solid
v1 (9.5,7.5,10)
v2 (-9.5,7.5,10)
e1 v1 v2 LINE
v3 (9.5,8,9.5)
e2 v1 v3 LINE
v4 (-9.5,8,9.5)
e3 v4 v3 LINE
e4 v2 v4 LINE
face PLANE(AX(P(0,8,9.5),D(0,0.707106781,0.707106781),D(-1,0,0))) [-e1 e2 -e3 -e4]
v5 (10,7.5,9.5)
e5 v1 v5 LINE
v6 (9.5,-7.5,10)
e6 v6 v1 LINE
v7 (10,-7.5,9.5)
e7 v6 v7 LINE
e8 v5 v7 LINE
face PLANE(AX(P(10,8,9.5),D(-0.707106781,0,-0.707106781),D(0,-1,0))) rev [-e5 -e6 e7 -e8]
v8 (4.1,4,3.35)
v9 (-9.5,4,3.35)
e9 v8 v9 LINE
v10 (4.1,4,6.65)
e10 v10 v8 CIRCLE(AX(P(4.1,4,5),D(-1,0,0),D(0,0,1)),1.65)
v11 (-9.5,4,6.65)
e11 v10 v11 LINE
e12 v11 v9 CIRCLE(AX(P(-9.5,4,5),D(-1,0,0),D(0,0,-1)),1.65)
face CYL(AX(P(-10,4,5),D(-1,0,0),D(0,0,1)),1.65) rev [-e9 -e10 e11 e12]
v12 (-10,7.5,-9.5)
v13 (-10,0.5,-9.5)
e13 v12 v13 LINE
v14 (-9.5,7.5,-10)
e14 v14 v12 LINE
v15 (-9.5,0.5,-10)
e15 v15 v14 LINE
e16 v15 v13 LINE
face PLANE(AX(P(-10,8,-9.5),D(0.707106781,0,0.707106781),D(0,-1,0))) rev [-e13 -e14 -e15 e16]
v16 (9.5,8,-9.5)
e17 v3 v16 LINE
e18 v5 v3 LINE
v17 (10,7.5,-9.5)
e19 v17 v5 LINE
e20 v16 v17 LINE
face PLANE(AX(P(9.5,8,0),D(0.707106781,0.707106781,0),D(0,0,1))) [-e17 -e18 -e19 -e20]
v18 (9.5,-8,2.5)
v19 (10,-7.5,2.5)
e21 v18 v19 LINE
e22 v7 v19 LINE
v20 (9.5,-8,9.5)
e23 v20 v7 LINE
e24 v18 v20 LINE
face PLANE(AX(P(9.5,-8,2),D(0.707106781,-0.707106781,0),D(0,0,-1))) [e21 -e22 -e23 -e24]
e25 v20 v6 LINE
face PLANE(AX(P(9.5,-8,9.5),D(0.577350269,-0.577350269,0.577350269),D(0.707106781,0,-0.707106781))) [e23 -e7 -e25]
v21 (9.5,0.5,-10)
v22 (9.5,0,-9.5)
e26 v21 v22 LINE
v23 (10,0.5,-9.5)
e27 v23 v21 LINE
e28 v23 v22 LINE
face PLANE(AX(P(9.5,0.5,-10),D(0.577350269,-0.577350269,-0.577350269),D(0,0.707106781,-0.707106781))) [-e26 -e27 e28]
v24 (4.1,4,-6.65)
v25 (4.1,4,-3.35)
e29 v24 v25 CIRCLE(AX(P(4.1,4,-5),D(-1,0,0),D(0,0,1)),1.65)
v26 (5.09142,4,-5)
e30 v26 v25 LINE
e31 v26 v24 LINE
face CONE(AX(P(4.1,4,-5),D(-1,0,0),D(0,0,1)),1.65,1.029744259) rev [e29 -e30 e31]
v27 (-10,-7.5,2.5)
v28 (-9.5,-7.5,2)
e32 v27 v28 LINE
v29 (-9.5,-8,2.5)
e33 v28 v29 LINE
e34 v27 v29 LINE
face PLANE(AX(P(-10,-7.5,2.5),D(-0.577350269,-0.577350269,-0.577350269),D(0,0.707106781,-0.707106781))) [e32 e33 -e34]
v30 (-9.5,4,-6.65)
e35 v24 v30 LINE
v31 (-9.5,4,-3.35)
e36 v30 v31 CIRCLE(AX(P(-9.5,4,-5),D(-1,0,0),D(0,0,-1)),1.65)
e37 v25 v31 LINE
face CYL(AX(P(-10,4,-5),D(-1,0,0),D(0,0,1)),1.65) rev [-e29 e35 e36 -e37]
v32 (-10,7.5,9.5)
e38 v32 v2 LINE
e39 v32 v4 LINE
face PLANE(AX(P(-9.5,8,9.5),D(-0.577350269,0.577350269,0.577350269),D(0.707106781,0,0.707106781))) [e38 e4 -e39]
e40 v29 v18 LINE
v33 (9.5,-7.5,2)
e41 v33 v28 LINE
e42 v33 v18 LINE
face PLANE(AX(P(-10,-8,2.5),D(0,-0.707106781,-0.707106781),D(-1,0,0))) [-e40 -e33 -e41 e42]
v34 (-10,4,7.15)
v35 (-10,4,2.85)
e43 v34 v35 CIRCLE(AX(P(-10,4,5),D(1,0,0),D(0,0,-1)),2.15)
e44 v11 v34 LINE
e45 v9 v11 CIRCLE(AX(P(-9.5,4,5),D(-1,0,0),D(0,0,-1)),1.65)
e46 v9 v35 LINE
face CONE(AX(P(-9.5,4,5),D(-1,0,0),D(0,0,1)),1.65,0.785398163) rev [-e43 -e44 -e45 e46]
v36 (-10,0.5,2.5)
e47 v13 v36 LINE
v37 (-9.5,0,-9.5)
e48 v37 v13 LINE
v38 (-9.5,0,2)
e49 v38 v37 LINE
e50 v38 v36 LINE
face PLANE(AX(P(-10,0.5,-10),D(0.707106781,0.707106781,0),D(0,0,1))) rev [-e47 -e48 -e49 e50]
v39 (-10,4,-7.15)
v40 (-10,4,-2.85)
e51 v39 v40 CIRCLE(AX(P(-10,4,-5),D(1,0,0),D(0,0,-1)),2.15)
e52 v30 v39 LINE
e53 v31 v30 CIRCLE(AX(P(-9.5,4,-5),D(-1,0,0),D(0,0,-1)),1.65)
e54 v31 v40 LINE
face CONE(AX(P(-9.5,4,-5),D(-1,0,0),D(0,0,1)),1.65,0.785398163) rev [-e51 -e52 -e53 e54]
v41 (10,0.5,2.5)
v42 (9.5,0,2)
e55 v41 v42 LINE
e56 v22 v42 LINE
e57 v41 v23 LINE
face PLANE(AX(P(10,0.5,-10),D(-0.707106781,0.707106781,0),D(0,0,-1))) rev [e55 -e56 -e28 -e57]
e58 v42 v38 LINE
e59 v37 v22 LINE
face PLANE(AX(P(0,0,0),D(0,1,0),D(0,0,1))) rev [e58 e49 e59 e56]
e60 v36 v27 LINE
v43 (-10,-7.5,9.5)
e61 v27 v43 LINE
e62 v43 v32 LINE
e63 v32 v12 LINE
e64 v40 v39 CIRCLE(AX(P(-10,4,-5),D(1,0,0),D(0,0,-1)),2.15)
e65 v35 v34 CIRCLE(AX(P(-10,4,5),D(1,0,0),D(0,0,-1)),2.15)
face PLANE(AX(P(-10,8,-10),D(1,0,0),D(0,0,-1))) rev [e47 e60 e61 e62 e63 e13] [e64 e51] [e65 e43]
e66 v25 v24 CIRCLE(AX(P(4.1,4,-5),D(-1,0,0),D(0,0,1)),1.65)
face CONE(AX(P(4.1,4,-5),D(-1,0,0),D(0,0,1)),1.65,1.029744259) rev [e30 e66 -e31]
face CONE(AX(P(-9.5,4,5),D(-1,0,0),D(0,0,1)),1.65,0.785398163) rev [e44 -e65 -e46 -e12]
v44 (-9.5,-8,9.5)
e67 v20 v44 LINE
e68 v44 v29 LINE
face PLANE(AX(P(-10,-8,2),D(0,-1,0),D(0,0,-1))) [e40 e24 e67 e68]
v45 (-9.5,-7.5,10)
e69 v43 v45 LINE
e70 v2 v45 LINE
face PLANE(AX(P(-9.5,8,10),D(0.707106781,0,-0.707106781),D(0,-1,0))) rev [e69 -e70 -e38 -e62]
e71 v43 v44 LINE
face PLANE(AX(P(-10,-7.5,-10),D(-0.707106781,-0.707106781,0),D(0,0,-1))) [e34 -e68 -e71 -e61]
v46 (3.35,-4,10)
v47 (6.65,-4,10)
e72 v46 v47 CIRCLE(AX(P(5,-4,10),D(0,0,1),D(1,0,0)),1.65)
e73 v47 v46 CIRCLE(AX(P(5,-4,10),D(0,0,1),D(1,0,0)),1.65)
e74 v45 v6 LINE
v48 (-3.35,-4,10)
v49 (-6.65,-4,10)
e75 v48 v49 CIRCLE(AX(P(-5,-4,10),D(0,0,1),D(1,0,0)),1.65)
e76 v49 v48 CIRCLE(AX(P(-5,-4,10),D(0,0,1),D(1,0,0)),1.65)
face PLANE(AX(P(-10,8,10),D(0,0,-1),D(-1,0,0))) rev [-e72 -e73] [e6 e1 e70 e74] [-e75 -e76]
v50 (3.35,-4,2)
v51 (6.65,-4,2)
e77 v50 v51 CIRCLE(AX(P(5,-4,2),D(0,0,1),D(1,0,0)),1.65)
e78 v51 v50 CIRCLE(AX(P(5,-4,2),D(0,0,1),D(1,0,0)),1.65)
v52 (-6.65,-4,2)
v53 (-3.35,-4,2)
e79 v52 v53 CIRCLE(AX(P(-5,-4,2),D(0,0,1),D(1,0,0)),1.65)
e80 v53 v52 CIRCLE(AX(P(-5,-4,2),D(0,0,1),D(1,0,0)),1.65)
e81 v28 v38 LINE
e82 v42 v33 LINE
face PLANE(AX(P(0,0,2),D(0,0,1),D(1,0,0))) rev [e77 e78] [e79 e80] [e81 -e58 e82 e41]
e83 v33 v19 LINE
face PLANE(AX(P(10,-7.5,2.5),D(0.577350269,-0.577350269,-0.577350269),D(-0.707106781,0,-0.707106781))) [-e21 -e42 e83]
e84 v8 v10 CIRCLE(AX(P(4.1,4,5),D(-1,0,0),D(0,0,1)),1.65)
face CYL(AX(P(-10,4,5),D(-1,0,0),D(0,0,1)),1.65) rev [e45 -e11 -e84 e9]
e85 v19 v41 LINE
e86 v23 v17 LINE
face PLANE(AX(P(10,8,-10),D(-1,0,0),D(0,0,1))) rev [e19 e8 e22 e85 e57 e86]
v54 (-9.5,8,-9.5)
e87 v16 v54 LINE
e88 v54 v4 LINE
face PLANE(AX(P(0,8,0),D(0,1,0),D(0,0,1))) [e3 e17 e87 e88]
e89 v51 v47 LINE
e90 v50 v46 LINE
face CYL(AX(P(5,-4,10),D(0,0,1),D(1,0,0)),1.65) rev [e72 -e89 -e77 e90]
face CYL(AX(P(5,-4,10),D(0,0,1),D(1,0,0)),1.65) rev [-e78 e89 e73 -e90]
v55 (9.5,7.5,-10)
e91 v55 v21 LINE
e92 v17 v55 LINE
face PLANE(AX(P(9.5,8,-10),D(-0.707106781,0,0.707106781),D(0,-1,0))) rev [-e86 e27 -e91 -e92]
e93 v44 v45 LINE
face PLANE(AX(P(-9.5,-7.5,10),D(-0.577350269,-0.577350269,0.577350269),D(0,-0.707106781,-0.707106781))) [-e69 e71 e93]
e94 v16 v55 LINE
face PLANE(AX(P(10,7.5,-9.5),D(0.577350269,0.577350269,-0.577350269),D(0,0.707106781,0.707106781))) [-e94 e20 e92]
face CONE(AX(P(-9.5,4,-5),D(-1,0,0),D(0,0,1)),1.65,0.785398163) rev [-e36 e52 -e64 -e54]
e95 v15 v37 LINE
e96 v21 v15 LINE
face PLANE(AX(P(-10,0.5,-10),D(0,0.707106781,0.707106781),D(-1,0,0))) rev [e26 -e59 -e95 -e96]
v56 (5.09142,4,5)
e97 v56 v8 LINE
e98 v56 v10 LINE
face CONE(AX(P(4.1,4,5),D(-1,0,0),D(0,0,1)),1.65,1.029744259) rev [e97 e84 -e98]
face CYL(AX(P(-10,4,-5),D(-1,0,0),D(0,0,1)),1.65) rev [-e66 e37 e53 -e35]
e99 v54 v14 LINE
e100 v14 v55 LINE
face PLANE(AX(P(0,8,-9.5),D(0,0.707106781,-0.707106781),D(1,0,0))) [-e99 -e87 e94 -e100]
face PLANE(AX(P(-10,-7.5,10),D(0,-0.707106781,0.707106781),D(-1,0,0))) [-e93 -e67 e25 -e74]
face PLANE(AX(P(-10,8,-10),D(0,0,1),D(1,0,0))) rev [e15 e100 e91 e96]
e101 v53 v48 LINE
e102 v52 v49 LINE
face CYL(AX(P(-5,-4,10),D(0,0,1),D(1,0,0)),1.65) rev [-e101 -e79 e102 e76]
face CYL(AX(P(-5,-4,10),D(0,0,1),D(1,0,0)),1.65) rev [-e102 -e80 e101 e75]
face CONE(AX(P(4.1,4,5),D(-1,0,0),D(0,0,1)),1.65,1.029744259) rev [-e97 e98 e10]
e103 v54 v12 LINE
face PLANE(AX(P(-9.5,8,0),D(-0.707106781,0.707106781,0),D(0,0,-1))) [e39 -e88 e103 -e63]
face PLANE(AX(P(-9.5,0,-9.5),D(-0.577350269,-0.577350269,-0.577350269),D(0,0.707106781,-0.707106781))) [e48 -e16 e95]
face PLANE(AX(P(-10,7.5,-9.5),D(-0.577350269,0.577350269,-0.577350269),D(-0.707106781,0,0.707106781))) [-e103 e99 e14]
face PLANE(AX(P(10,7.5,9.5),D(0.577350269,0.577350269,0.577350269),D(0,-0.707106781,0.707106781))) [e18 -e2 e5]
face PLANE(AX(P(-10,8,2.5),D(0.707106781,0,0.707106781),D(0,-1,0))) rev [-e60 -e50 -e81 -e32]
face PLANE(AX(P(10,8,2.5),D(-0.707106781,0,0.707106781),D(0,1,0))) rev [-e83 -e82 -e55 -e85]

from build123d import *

# Parameters (mm, degrees)
SKETCH_1_W             = 20
SKETCH_1_H             = 20
EXTRUDE_1_DEPTH        = 8
HOLE_WIZARD_M4_1_D     = 3.3
HOLE_WIZARD_M4_1_DEPTH = 14.1
HOLE_WIZARD_M4_1_TIP   = 0.991420021
SKETCH_6_W             = 20
SKETCH_6_H             = 8
EXTRUDE_2_DEPTH        = 8
HOLE_WIZARD_M4_3_D     = 3.3
HOLE_WIZARD_M4_3_DEPTH = 14.1
HOLE_WIZARD_M4_3_TIP   = 0.991420021
CHAMFER_2_SIZE         = 0.5


with BuildPart() as part:
    # 草图1 → 凸台-拉伸1 (new body)
    with BuildSketch(Plane(origin=(0, 0, 0), x_dir=(1, 0, 0), z_dir=(0, 1, 0))):
        Rectangle(SKETCH_1_W, SKETCH_1_H)
    extrude(amount=EXTRUDE_1_DEPTH)

    # M4 螺纹孔1
    with Locations(Plane(origin=(-10, -0.113114855, 4.919036023), x_dir=(0, 0, -1), z_dir=(-1, 0, 0))):
        with Locations((9.919036023, -4.113114855), (-0.080963977, -4.113114855)):
            Hole(HOLE_WIZARD_M4_1_D / 2, depth=HOLE_WIZARD_M4_1_DEPTH)
            with Locations((0, 0, -(HOLE_WIZARD_M4_1_DEPTH + HOLE_WIZARD_M4_1_TIP / 2))):  # 118° drill point
                Cone(0, HOLE_WIZARD_M4_1_D / 2, HOLE_WIZARD_M4_1_TIP, mode=Mode.SUBTRACT)

    # 草图6 → 凸台-拉伸2 (add)
    with BuildSketch(Plane.XY.offset(10)):
        with Locations((0, -4)):
            Rectangle(SKETCH_6_W, SKETCH_6_H)
    extrude(amount=-EXTRUDE_2_DEPTH)

    # M4 螺纹孔3
    with Locations(Plane.XY.offset(10)):
        with Locations((-5, -4), (5, -4)):
            Hole(HOLE_WIZARD_M4_3_D / 2, depth=HOLE_WIZARD_M4_3_DEPTH)
            with Locations((0, 0, -(HOLE_WIZARD_M4_3_DEPTH + HOLE_WIZARD_M4_3_TIP / 2))):  # 118° drill point
                Cone(0, HOLE_WIZARD_M4_3_D / 2, HOLE_WIZARD_M4_3_TIP, mode=Mode.SUBTRACT)

    # 倒角2
    chamfer_2_edges = [part.edges().sort_by_distance(p)[0] for p in [
        (-10, 8, 0),
        (-10, 0, 10),
        (-10, -4, 2),
        (-10, 0, -4),
        (10, 4, -10),
        (0, 8, -10),
        (-10, 4, -10),
        (0, 0, -10),
        (10, -8, 6),
        (10, 0, -4),
        (10, -4, 2),
        (0, -8, 2),
        (-10, -8, 6),
        (0, -8, 10),
        (10, 8, 0),
        (0, 8, 10),
        (10, 0, 10),
        (-10, 4, 3.35),
        (-10, 4, -6.65),
    ]]
    chamfer(chamfer_2_edges, length=CHAMFER_2_SIZE)


solid = part.part
